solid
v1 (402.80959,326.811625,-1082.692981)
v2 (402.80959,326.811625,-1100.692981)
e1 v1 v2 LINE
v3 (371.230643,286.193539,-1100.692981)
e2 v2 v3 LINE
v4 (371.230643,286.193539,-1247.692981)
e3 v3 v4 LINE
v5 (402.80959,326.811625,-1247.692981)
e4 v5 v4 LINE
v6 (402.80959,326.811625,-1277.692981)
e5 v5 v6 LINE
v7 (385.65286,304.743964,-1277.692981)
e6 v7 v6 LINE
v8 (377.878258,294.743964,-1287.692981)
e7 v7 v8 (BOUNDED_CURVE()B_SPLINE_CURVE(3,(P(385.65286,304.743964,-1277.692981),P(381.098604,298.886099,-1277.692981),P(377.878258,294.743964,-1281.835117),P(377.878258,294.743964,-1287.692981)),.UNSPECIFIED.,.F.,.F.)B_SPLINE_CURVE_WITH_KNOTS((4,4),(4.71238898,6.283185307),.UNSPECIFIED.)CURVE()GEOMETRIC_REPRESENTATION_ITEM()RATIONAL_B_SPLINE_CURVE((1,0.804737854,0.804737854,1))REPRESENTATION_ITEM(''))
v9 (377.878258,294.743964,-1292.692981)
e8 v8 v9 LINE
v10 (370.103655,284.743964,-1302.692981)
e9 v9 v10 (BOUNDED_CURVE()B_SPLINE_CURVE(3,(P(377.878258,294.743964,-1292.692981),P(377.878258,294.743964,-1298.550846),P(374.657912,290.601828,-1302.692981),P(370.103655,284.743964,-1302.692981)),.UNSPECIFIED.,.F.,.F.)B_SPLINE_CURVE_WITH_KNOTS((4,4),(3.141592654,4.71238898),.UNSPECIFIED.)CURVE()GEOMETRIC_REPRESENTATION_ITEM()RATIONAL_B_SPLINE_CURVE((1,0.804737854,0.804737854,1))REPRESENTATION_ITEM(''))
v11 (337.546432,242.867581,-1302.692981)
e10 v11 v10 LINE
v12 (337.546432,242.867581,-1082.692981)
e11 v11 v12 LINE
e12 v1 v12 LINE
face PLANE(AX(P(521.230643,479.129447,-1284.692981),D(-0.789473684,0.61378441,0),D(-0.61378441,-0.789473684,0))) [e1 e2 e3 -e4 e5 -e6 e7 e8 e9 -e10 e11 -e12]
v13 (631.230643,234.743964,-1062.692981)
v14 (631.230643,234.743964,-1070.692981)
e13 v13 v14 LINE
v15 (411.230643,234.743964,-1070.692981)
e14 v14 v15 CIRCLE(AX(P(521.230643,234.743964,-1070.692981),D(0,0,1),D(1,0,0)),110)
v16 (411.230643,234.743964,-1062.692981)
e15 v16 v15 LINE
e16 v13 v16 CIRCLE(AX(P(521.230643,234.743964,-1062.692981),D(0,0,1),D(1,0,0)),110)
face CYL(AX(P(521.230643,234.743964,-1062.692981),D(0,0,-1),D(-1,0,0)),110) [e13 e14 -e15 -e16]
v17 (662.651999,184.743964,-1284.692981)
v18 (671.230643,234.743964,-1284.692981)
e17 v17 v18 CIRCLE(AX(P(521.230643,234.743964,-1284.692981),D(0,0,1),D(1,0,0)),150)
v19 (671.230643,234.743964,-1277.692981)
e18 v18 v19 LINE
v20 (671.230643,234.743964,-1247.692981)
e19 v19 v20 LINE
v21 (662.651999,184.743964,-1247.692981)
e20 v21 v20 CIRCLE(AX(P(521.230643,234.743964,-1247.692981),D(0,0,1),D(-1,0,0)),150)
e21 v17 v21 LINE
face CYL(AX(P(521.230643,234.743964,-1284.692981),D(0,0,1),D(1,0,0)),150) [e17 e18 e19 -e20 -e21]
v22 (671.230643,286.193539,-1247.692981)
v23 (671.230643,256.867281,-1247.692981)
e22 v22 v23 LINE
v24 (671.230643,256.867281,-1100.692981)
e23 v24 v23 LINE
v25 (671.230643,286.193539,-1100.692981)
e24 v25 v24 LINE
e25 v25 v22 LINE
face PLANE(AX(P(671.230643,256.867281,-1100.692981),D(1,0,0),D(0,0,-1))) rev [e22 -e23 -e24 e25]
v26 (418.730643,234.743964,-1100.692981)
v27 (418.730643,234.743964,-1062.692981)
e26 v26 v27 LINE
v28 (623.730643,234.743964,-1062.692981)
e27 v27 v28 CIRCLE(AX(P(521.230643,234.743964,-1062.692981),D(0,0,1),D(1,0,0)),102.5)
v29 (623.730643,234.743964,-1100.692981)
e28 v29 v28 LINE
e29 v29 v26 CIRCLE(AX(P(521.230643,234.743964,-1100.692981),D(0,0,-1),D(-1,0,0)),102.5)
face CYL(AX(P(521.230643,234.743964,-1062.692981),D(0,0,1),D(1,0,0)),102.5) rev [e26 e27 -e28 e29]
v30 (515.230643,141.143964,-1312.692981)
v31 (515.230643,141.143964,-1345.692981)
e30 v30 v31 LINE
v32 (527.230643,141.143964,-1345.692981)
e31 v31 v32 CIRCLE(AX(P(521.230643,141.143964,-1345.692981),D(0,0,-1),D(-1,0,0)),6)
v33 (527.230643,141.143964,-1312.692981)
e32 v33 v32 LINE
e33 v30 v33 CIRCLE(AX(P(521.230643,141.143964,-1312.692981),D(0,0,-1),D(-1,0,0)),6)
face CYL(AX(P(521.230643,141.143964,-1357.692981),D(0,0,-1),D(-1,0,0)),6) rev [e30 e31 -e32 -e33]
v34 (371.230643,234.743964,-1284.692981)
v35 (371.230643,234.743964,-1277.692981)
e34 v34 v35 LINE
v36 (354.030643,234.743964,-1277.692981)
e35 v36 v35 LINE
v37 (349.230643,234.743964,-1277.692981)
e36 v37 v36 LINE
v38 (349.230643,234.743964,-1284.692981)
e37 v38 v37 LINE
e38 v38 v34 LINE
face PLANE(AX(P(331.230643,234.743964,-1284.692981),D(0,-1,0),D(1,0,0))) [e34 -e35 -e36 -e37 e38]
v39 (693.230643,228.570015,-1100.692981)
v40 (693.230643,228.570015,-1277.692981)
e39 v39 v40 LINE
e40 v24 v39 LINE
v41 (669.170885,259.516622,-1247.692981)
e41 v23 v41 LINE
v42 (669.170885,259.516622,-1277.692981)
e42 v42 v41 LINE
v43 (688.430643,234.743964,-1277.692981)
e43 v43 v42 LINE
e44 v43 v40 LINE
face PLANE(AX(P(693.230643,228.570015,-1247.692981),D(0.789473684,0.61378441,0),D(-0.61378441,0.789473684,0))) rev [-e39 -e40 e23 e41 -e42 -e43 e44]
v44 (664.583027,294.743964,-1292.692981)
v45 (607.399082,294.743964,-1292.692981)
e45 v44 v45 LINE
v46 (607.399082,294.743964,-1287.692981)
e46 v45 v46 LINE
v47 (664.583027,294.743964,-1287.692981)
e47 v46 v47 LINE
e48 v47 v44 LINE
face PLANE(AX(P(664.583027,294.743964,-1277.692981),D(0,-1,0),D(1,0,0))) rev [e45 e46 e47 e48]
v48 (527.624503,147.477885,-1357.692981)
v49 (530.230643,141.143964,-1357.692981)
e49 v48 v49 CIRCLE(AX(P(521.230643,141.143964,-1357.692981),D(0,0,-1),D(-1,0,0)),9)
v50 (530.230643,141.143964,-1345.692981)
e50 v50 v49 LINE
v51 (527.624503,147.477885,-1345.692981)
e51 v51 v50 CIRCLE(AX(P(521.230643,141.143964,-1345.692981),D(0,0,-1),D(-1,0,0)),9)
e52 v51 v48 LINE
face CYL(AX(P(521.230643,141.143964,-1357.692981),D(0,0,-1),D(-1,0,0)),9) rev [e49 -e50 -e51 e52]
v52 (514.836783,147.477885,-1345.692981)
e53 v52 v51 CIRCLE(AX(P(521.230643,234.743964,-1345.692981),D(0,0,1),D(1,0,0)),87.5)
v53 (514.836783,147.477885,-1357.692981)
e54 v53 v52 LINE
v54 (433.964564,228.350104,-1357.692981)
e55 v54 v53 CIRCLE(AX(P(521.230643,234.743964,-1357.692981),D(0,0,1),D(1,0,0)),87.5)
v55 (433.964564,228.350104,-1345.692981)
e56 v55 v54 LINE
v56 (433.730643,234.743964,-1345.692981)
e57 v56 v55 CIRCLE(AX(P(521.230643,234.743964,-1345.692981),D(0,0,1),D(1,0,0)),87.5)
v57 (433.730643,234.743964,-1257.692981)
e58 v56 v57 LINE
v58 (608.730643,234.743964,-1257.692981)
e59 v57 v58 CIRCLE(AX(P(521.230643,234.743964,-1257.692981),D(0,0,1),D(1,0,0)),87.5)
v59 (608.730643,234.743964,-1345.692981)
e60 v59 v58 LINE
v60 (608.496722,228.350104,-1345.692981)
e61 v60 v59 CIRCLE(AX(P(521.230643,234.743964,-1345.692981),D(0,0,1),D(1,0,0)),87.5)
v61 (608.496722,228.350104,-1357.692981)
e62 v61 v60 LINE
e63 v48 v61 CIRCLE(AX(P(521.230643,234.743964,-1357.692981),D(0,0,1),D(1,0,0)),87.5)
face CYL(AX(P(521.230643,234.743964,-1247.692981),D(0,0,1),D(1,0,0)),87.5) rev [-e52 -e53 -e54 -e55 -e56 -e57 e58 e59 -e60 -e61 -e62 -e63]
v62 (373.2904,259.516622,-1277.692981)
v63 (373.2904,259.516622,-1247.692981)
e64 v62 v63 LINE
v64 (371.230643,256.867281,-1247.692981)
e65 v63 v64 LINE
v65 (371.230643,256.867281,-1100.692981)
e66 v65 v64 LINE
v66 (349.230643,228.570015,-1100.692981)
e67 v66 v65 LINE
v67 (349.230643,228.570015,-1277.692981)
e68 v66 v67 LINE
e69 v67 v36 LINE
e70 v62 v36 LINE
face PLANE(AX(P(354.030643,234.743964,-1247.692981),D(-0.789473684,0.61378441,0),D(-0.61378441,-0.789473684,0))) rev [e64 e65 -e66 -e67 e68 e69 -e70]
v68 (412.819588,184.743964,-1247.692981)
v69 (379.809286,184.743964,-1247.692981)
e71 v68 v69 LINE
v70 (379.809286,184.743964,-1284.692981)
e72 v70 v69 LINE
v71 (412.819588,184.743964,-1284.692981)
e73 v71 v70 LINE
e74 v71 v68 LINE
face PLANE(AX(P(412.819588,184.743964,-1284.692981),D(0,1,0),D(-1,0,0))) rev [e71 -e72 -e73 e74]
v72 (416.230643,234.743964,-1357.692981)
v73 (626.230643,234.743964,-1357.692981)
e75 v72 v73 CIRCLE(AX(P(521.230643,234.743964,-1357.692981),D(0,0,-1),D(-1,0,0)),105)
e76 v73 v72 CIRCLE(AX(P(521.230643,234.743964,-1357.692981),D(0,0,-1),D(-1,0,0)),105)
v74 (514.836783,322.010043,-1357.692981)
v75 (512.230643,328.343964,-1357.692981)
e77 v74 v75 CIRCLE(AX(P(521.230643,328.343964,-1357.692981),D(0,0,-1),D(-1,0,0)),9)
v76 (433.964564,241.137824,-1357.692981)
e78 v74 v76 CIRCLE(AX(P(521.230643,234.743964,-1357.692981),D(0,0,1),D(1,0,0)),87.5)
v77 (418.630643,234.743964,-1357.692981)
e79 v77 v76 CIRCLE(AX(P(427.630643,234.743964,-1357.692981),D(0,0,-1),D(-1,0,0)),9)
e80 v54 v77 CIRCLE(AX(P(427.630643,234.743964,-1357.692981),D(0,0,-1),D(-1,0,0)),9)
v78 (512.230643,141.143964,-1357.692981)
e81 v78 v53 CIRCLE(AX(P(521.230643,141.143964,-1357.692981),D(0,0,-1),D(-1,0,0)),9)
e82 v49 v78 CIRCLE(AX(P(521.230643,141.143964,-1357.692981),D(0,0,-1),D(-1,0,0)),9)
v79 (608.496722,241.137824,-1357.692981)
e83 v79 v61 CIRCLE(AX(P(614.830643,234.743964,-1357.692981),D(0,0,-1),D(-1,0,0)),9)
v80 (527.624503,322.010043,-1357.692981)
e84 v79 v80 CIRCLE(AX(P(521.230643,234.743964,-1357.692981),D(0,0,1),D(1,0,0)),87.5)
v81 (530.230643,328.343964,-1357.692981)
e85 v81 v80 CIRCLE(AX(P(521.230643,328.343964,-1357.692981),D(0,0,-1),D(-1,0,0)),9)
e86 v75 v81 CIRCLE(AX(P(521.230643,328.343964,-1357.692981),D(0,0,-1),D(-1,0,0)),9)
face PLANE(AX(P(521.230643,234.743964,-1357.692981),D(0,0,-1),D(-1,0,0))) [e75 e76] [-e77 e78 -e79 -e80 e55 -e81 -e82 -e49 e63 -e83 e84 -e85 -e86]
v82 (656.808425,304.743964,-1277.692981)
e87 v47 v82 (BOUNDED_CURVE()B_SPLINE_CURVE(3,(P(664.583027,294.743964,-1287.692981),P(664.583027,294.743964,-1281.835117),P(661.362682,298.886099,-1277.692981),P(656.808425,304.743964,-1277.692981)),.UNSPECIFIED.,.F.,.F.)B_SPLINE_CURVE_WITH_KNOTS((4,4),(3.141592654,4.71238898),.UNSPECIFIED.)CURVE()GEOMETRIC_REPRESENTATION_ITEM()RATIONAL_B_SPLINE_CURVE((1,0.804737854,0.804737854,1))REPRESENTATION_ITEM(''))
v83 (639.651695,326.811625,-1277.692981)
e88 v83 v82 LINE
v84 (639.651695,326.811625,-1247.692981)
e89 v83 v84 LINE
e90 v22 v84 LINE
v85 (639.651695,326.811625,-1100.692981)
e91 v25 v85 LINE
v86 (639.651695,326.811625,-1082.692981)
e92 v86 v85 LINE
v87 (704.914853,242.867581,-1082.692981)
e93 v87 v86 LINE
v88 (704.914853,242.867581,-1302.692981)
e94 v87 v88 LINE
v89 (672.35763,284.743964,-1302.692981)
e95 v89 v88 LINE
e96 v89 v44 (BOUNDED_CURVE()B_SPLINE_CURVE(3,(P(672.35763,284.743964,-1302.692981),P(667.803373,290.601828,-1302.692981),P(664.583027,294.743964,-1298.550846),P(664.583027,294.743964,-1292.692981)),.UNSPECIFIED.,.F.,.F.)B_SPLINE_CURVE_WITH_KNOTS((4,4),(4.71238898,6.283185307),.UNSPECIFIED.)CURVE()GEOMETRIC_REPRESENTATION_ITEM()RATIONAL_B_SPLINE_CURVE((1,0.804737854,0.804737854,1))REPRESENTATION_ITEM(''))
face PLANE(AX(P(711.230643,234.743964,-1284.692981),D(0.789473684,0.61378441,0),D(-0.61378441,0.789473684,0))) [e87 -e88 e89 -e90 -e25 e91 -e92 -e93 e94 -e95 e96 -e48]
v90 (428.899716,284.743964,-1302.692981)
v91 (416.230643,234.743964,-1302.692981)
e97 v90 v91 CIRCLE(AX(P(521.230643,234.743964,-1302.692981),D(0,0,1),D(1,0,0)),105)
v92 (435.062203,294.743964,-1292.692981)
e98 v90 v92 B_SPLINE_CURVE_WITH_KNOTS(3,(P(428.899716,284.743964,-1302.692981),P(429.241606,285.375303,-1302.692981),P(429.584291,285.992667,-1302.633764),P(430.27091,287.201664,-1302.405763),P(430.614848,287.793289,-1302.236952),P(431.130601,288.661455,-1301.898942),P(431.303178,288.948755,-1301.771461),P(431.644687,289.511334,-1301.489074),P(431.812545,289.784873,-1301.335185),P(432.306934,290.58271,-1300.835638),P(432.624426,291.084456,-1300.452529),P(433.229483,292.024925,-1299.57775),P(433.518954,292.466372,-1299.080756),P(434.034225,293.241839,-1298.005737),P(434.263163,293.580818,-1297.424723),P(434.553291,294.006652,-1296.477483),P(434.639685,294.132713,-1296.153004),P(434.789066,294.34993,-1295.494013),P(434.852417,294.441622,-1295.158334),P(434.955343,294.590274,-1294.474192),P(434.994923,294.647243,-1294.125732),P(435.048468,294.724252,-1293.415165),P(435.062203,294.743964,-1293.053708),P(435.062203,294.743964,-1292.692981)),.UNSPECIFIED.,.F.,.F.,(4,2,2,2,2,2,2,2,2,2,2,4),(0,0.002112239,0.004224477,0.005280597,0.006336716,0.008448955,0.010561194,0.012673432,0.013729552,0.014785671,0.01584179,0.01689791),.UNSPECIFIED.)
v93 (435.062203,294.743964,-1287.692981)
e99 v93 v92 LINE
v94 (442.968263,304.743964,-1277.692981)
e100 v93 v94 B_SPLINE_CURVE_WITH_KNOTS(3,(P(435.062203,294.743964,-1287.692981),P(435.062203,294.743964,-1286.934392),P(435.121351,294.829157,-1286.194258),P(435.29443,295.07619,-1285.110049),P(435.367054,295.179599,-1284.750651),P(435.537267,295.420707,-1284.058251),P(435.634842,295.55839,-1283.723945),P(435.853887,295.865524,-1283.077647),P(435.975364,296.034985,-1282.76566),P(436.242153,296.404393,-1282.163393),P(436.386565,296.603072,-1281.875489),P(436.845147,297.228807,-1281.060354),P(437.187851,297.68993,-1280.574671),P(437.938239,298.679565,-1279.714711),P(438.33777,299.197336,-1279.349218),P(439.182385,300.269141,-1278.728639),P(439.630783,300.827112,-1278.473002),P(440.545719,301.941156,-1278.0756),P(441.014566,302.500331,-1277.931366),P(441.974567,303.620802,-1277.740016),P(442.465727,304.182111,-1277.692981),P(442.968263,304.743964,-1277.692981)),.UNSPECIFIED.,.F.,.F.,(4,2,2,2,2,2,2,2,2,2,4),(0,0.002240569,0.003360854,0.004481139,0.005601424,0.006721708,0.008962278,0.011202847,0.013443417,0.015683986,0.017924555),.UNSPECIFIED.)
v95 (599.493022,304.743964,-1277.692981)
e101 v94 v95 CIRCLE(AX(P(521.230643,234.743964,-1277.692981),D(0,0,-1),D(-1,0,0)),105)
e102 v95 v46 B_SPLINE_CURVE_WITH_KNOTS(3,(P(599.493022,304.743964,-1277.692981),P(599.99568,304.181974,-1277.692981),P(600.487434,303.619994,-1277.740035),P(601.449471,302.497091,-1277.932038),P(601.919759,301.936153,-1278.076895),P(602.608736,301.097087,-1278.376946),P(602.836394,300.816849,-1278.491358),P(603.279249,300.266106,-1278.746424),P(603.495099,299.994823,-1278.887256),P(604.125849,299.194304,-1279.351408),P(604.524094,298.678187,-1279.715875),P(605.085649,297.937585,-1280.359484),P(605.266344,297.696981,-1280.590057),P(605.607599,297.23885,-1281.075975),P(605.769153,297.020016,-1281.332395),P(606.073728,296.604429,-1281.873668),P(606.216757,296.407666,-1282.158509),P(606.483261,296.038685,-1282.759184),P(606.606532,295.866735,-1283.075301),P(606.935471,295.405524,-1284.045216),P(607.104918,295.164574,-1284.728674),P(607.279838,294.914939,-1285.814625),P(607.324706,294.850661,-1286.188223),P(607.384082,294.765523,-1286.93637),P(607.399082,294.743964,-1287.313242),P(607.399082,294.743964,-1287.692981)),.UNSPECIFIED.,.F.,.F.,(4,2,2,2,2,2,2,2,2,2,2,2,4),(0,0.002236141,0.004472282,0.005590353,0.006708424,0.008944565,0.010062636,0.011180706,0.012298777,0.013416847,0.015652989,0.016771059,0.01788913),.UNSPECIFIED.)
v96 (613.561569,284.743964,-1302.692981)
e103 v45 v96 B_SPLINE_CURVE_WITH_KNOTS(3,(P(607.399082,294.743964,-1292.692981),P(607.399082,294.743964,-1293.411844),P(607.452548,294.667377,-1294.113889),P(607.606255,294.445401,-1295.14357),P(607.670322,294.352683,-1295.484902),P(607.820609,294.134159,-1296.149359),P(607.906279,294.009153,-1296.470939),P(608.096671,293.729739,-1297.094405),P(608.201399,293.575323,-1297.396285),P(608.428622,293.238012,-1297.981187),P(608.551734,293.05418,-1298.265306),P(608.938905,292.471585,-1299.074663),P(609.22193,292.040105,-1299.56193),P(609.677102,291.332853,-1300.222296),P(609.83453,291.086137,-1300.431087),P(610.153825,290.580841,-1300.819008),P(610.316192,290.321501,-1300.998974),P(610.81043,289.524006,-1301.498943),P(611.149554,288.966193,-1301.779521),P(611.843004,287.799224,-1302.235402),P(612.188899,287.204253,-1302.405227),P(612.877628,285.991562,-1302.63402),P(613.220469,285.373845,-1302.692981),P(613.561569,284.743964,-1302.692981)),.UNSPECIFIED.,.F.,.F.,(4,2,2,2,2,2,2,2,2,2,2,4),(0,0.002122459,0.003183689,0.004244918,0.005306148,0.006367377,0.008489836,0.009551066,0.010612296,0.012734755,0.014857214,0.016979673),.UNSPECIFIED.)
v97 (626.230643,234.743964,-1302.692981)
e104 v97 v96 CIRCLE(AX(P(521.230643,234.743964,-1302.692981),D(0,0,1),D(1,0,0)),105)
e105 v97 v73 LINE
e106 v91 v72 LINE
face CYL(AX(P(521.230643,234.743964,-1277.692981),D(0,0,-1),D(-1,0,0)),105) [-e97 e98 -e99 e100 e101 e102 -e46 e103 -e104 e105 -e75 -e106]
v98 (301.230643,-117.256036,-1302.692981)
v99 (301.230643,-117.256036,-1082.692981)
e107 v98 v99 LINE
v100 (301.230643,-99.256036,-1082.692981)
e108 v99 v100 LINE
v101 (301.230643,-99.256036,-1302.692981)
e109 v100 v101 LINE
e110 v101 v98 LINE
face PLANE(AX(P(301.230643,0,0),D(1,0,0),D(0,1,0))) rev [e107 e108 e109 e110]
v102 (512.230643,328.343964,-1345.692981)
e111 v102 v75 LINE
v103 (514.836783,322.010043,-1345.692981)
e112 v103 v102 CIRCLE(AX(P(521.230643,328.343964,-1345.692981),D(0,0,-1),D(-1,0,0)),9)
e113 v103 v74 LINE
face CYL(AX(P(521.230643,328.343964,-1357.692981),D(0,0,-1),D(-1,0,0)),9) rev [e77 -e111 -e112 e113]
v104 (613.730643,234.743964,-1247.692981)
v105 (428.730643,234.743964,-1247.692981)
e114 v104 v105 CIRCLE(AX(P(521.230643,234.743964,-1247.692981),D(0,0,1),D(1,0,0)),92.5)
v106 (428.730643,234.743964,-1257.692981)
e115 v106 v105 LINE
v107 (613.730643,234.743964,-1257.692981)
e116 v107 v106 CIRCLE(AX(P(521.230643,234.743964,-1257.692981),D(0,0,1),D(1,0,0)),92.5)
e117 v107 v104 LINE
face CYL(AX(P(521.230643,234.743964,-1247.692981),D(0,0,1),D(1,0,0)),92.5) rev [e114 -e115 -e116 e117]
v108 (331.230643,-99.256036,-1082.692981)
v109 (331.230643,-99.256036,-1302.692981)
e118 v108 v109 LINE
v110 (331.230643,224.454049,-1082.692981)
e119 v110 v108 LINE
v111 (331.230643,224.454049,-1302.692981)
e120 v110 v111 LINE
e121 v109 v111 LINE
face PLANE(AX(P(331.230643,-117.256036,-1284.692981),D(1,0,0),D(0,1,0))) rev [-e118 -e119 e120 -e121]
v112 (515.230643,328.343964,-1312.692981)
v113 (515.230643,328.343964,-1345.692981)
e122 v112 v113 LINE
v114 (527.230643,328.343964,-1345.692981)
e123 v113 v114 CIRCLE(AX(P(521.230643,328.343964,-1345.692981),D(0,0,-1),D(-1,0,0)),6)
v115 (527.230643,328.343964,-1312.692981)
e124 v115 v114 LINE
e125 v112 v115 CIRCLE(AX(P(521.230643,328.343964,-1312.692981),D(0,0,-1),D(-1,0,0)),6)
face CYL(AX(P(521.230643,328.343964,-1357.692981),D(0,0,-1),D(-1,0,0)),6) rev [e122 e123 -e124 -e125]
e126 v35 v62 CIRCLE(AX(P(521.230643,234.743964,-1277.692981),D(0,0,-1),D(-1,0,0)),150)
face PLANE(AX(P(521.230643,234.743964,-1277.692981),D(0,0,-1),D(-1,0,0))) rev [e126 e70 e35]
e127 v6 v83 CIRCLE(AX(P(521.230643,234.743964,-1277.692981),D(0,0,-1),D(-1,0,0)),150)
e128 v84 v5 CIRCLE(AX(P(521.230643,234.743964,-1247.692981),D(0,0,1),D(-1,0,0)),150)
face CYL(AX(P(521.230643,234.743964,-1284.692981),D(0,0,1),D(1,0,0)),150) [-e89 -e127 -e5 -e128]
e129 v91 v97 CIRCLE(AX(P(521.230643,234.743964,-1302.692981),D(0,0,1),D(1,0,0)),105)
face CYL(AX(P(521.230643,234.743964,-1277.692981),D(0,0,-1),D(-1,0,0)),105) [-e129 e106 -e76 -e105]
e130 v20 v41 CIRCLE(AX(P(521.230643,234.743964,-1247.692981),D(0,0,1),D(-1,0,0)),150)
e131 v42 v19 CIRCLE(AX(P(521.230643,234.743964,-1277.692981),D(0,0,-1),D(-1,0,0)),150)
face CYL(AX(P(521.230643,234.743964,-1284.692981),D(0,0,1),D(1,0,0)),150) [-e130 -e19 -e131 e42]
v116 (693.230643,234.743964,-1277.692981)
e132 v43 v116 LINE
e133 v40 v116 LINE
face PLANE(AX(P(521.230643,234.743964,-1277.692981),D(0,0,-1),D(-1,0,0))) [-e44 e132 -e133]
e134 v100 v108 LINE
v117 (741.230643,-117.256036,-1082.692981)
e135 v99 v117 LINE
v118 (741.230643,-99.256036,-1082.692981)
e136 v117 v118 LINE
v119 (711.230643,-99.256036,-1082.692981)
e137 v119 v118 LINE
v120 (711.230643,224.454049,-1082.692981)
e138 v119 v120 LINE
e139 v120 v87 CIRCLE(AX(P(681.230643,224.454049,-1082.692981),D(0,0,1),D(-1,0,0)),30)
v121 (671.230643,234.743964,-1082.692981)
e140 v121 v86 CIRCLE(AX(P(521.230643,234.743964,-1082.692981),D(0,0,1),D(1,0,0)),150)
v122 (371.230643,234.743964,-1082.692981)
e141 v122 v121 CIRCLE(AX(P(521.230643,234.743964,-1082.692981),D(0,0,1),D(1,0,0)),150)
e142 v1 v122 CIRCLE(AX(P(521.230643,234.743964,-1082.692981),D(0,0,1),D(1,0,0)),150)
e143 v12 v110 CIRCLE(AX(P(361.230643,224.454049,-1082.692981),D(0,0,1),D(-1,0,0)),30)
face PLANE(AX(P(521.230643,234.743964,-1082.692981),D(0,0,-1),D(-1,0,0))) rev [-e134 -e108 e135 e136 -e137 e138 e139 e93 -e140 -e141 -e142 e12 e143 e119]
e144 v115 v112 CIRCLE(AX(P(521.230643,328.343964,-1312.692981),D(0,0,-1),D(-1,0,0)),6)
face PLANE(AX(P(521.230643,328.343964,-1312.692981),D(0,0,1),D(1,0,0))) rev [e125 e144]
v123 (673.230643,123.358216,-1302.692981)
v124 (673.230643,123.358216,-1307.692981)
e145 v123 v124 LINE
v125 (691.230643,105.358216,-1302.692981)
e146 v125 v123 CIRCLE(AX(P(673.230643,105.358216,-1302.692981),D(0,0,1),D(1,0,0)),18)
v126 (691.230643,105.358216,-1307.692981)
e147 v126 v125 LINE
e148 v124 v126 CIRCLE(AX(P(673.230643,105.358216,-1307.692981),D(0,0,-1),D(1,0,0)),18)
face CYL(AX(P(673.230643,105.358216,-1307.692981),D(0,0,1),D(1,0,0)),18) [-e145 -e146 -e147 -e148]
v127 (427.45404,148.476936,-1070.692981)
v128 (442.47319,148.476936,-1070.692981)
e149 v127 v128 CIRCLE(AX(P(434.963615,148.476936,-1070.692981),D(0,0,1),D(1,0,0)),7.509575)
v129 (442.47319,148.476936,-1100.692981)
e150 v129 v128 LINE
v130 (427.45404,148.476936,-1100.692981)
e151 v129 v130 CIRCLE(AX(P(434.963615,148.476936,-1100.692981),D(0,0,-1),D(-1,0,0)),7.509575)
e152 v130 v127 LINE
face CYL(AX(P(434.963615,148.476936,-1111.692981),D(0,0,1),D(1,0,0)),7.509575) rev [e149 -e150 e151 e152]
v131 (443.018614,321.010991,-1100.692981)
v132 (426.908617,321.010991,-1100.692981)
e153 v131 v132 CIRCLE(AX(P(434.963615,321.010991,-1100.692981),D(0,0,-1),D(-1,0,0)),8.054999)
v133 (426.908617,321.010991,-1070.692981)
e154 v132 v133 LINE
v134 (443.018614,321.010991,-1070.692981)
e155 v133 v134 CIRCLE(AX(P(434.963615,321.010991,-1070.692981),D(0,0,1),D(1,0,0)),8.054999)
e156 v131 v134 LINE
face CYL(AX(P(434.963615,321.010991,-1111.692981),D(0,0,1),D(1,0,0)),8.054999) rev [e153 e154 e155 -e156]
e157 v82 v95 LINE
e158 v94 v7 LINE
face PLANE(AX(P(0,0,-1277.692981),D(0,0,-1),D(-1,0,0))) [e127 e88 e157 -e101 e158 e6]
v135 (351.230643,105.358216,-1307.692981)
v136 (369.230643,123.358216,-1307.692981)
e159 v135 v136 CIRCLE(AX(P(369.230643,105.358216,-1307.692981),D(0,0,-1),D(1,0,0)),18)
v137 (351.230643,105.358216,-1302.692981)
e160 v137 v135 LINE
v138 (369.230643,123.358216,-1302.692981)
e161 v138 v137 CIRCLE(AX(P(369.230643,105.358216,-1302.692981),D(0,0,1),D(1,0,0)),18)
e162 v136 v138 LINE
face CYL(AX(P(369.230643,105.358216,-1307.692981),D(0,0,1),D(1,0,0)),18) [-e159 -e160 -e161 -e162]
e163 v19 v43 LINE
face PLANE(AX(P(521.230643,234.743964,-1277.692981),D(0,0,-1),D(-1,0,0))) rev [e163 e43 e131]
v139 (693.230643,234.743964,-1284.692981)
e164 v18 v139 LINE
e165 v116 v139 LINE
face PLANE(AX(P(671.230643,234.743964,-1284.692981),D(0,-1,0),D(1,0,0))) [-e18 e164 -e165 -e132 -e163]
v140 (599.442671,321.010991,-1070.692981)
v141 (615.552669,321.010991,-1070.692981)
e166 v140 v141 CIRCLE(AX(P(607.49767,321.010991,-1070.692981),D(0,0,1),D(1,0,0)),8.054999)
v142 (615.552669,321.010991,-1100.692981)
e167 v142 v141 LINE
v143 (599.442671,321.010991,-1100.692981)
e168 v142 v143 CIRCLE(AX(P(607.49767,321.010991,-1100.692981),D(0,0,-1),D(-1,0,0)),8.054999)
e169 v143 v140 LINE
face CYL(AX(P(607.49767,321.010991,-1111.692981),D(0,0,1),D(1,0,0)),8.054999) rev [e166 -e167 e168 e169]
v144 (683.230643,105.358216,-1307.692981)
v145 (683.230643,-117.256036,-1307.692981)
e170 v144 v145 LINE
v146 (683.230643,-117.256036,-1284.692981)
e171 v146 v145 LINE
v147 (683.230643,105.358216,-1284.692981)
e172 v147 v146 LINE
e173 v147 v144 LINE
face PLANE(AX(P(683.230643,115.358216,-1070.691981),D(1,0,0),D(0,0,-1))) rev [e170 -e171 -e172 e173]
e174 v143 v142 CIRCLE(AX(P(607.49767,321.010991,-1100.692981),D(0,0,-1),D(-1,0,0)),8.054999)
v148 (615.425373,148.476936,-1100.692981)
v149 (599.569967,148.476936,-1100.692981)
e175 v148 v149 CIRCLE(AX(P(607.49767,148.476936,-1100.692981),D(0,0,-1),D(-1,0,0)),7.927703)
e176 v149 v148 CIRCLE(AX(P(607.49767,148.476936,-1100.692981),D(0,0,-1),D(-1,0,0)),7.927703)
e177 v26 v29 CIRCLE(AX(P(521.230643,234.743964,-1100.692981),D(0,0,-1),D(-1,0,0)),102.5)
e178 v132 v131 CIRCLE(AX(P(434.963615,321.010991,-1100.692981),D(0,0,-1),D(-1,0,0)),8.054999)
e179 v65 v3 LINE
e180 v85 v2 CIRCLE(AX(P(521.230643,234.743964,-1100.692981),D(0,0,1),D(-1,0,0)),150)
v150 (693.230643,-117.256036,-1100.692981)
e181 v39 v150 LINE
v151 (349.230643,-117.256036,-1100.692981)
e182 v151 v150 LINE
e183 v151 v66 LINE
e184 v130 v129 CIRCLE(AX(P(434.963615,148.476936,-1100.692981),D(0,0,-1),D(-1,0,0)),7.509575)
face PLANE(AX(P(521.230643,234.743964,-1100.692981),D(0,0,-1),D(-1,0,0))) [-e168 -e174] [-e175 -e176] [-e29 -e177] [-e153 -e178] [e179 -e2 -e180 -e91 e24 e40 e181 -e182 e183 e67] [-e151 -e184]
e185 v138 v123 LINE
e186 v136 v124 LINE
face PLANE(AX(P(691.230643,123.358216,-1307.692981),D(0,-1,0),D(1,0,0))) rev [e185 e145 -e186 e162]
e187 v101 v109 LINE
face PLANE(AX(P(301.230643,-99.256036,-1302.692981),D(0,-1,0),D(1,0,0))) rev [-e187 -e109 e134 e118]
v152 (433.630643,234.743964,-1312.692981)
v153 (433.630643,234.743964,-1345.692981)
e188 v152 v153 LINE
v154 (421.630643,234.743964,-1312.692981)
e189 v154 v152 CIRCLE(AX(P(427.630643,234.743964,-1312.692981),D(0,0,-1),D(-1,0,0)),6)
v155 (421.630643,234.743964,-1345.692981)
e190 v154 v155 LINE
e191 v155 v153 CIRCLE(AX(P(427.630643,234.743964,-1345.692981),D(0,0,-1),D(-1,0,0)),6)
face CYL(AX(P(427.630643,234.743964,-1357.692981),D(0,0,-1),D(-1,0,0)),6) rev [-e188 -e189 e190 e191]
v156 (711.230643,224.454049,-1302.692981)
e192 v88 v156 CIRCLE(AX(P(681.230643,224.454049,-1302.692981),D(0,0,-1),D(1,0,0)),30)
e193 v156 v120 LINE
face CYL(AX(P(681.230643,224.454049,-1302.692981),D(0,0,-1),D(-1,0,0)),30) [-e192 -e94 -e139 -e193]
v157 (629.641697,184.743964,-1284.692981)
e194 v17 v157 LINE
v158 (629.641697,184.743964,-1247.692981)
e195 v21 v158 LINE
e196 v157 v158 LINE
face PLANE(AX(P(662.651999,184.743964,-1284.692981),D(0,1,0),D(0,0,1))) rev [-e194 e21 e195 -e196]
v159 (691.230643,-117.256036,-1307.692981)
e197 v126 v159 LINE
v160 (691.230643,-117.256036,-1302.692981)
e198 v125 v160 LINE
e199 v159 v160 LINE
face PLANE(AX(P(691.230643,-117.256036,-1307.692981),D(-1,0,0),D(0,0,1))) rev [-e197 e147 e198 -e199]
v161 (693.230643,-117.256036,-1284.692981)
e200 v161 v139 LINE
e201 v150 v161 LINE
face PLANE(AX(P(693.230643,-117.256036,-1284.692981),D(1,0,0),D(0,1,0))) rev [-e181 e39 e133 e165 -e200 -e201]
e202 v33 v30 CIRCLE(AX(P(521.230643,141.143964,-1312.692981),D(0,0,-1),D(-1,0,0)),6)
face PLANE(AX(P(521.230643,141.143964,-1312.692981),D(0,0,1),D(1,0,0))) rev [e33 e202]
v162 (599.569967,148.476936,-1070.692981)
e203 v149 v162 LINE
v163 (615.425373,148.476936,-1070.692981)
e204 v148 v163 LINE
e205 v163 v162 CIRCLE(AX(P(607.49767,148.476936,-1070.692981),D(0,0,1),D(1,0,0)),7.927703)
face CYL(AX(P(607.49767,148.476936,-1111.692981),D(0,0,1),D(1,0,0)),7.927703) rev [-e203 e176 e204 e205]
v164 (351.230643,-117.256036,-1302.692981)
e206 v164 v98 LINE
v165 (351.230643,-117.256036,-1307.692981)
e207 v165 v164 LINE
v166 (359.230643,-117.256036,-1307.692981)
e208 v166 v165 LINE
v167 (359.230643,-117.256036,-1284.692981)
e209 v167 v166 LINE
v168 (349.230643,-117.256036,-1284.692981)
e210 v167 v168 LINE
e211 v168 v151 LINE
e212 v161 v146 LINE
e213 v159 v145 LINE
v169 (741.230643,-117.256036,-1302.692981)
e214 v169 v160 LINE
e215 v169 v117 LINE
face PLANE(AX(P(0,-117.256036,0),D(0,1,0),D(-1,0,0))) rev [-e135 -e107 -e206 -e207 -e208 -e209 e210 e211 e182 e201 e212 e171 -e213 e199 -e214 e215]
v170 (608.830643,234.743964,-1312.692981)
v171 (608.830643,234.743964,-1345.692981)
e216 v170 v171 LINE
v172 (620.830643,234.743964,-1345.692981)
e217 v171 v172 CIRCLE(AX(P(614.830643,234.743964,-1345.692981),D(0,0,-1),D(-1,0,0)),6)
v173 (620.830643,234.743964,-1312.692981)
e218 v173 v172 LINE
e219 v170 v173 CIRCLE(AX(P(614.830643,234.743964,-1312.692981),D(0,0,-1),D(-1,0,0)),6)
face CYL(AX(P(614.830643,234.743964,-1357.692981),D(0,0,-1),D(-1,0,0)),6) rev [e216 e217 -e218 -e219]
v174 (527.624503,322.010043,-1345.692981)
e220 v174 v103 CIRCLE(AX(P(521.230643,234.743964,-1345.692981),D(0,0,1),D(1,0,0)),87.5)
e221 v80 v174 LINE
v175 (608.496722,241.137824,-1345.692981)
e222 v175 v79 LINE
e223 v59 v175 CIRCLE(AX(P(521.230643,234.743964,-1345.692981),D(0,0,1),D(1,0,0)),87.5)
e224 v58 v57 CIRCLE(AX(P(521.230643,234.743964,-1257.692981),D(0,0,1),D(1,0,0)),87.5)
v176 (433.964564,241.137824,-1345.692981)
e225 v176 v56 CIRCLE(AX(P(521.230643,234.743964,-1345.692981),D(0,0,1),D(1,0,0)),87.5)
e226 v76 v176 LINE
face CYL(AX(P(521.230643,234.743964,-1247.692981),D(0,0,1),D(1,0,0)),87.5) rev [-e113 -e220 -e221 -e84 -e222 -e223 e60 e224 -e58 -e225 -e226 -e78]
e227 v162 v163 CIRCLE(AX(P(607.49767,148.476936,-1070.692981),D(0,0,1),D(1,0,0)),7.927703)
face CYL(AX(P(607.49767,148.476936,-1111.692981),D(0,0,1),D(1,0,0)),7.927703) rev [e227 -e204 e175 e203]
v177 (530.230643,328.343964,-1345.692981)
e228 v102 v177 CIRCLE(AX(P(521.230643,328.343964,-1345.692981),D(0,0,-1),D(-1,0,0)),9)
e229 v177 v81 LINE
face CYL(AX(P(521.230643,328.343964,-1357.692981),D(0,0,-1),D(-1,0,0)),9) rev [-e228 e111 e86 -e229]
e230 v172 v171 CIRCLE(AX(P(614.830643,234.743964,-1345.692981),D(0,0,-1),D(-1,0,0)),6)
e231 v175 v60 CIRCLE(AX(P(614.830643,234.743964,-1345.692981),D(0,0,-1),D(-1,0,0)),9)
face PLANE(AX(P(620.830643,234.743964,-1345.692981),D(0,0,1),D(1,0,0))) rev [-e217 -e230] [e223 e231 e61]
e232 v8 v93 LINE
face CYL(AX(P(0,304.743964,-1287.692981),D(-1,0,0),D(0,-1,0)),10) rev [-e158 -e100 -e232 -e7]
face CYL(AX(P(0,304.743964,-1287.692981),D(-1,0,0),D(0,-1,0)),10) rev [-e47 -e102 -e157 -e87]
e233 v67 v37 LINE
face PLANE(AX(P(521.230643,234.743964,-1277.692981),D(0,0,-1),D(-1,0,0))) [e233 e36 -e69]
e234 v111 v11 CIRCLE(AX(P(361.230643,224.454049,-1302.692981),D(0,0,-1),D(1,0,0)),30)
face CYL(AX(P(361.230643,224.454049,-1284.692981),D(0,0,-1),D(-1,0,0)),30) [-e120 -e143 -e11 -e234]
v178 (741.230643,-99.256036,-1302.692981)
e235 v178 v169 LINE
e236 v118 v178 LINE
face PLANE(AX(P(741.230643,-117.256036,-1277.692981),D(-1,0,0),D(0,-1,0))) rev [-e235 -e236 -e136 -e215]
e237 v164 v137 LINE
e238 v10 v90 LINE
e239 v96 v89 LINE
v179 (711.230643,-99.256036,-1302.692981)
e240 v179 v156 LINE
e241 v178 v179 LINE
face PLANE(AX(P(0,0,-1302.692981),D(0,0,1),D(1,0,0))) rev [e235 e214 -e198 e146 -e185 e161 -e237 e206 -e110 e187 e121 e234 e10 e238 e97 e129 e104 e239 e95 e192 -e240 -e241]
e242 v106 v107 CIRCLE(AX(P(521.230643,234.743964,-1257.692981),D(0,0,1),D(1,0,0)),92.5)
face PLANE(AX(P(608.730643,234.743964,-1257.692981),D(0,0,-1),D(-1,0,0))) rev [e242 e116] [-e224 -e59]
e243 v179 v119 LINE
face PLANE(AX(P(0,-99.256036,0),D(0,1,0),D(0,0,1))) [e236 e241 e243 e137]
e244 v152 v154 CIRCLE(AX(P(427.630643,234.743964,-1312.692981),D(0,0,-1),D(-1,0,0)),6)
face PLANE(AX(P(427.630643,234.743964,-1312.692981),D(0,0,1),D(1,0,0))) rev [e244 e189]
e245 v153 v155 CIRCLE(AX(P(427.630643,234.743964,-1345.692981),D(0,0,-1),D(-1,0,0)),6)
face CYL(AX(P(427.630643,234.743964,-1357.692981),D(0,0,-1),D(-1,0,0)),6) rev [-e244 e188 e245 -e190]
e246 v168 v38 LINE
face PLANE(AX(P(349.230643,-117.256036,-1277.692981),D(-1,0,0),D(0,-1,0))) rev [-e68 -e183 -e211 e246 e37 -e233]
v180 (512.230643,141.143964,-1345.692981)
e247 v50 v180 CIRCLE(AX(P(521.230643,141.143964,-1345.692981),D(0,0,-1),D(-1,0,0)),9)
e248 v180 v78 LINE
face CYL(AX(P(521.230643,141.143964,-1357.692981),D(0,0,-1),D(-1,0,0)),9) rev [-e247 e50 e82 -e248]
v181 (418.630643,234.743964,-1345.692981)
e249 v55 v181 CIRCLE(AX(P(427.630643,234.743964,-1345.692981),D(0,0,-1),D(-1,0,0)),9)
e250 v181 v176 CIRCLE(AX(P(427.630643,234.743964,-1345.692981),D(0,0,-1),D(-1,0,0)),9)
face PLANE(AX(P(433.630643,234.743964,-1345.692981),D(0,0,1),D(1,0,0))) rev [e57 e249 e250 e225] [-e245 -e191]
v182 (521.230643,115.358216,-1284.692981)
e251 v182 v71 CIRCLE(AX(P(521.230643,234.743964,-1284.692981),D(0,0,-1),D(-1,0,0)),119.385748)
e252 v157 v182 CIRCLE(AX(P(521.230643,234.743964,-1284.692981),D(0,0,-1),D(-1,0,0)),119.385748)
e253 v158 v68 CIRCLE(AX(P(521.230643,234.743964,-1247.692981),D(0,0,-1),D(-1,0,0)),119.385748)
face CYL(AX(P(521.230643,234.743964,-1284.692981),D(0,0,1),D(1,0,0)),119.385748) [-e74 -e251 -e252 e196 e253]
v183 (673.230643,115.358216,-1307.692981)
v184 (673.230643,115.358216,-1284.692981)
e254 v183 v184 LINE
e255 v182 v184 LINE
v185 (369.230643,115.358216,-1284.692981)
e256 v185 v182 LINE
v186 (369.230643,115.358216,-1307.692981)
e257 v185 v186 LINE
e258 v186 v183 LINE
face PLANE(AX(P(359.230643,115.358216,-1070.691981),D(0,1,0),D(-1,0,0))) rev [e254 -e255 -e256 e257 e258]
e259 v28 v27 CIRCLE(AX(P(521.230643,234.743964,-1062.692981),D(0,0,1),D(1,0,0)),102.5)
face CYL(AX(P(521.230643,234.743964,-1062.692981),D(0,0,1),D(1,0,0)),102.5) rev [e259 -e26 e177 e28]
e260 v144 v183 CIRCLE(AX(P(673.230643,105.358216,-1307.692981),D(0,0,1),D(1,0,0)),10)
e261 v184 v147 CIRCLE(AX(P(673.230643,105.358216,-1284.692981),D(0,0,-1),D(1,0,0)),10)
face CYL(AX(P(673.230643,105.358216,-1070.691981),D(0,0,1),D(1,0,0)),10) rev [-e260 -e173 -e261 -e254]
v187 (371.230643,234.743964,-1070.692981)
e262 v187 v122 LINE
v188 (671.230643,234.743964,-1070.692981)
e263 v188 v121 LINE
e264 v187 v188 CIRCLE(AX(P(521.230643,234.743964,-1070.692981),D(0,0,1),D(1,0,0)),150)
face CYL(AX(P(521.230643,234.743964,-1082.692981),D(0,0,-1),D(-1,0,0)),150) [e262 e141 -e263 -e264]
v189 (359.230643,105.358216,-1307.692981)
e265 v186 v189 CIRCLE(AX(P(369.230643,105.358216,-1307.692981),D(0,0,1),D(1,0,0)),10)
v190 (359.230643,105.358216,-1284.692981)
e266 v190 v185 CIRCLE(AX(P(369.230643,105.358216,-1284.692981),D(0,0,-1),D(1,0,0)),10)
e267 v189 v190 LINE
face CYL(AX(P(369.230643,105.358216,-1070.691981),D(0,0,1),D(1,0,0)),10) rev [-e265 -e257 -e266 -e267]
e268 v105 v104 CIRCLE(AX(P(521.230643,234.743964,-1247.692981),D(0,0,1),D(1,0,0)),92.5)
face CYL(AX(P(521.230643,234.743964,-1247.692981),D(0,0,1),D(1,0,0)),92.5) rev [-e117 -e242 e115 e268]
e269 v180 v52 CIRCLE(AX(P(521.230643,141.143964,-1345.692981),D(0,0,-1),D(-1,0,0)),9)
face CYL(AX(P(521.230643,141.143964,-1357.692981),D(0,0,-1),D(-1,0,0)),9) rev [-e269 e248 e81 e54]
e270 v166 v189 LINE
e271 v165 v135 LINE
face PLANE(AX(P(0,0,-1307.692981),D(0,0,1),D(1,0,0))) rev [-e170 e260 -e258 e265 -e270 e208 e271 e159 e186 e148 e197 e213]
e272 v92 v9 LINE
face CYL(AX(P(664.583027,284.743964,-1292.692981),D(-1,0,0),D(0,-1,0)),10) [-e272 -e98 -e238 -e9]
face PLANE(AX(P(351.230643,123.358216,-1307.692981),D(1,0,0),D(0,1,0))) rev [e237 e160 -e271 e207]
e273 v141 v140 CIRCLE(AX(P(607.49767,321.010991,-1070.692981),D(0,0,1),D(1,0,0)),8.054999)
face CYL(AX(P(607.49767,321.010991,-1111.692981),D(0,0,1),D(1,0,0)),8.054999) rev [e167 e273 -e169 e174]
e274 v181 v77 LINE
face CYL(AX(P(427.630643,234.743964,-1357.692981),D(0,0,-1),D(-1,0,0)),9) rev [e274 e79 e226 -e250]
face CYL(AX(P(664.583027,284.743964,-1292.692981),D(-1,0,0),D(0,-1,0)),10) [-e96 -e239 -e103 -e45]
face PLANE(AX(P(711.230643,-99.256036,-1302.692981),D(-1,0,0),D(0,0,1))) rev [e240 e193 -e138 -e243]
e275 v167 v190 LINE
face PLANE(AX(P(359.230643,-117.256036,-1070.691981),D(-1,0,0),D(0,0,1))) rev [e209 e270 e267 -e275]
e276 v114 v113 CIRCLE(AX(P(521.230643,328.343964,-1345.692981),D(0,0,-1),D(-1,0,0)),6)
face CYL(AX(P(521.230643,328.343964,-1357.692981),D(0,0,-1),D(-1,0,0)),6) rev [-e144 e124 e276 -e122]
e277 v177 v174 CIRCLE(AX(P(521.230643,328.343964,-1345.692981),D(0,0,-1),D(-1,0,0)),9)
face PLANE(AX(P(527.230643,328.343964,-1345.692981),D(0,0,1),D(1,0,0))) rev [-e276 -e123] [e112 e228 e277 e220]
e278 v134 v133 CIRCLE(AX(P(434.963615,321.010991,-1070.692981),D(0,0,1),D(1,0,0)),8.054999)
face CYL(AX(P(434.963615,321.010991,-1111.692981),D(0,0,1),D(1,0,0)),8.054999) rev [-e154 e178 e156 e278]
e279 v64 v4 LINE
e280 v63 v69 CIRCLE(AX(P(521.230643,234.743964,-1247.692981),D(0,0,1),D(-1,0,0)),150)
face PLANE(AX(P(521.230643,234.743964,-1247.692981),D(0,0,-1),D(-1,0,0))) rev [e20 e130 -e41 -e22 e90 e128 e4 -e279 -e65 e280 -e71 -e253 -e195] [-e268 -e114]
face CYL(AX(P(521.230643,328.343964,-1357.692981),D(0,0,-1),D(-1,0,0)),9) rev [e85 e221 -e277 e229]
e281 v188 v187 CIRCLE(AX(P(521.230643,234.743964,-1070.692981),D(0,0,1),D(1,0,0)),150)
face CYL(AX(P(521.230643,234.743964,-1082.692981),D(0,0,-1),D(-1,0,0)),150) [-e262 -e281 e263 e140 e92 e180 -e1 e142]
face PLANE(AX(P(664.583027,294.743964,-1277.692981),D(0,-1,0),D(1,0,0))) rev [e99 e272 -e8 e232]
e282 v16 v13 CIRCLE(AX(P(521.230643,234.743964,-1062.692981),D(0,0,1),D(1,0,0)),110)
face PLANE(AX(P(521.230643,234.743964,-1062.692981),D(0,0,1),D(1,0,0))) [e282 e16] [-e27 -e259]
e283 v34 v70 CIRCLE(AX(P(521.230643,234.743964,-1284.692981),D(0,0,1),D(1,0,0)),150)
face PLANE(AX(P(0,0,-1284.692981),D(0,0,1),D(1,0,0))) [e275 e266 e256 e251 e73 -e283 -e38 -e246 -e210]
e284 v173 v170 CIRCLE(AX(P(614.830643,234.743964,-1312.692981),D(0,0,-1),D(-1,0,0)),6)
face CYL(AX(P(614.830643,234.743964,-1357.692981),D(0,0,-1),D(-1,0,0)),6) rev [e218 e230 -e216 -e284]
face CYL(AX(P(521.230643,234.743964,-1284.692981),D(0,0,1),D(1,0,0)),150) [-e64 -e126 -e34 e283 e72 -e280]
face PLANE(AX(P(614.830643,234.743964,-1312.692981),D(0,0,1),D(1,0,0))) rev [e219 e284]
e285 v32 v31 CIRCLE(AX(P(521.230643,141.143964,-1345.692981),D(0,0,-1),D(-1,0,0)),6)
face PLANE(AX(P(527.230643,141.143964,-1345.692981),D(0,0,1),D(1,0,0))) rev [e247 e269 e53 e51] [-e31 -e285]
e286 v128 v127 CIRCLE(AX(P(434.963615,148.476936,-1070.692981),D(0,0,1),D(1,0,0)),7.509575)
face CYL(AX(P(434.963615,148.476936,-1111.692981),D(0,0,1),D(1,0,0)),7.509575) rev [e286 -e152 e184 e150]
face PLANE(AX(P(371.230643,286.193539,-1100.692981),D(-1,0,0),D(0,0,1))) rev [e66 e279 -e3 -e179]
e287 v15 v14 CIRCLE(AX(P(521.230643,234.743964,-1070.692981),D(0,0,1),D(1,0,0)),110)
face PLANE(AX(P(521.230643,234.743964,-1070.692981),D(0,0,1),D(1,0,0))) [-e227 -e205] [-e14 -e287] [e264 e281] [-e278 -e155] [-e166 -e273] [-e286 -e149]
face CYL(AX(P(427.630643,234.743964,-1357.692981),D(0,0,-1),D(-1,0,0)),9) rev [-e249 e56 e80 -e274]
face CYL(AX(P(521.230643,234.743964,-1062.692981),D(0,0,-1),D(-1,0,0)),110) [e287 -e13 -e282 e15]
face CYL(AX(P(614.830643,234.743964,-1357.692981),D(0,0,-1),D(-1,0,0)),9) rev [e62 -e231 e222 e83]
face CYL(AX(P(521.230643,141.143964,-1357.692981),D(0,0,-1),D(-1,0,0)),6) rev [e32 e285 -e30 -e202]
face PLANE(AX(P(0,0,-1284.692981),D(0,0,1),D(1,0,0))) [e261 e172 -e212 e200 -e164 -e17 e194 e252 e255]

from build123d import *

# Parameters (mm, degrees)
BOSS_EXTRUDE1_DEPTH               = 7
SKETCH2_W                         = 48
SKETCH2_H                         = 7
BOSS_EXTRUDE2_DEPTH               = 352
SKETCH3_W                         = 18
SKETCH3_H                         = 7
BOSS_EXTRUDE3_DEPTH               = 352
BOSS_EXTRUDE4_DEPTH               = 18
BOSS_EXTRUDE5_START               = 30
BOSS_EXTRUDE5_DEPTH               = 30
BOSS_EXTRUDE6_DEPTH               = 147
BOSS_EXTRUDE7_DEPTH               = 147
BOSS_EXTRUDE8_START               = 18
BOSS_EXTRUDE8_DEPTH               = 18
SKETCH9_W                         = 30
SKETCH9_H                         = 220
CUT_EXTRUDE1_DEPTH                = 334
CUT_EXTRUDE2_DEPTH                = 30
CUT_EXTRUDE3_DEPTH                = 30
SKETCH12_W                        = 220
SKETCH12_H                        = 18
BOSS_EXTRUDE9_DEPTH               = 30
BOSS_EXTRUDE10_START              = 12
SKETCH13_R                        = 150
BOSS_EXTRUDE10_DEPTH              = 12
CUT_EXTRUDE4_DEPTH                = 37
SKETCH15_W                        = 340
SKETCH15_H                        = 240.614252285
BOSS_EXTRUDE11_DEPTH              = 5
CUT_EXTRUDE5_REACH                = 915.869
SKETCH16_W                        = 324
SKETCH16_H                        = 232.614252285
CUT_EXTRUDE6_DEPTH                = 25
SKETCH18_R                        = 110
BOSS_EXTRUDE12_DEPTH              = 8
SKETCH19_W                        = 105
SKETCH19_H                        = 80
HOLE1_D                           = 205
HOLE1_DEPTH                       = 38
M10_COUNTERBORE_HOLE1_D           = 12
M10_COUNTERBORE_HOLE1_DEPTH       = 45
M10_COUNTERBORE_HOLE1_CBORE_D     = 18
M10_COUNTERBORE_HOLE1_CBORE_DEPTH = 12
HOLE2_D                           = 175
HOLE2_CBORE_D                     = 185
HOLE2_CBORE_DEPTH                 = 10
FILLET1_R                         = 10
FILLET2_R                         = 18
FILLET3_R                         = 30
FILLET4_R                         = 150
SKETCH26_R                        = 8.054998693
SKETCH26_R_2                      = 7.927703382
SKETCH26_R_3                      = 7.509574851
CUT_EXTRUDE8_DEPTH                = 41


with BuildPart() as part:
    # Sketch1 → Boss-Extrude1 (new body)
    with BuildSketch(Plane.XY.offset(-1277.692981355)):
        with BuildLine():
            Line((671.230642584, 234.743963655), (711.230642584, 234.743963655))
            Line((711.230642584, 234.743963655), (521.230642584, 479.129447483))
            Line((521.230642584, 479.129447483), (331.230642584, 234.743963655))
            Line((331.230642584, 234.743963655), (371.230642584, 234.743963655))
            ThreePointArc((371.230642584, 234.743963655), (521.230642584, 84.743963655), (671.230642584, 234.743963655))
        make_face()
    extrude(amount=-BOSS_EXTRUDE1_DEPTH)

    # Sketch2 → Boss-Extrude2 (add)
    with BuildSketch(Plane.XZ.offset(-234.743963655)):
        with Locations((717.230642584, -1281.192981355)):
            Rectangle(SKETCH2_W, SKETCH2_H)
    extrude(amount=BOSS_EXTRUDE2_DEPTH)

    # Sketch3 → Boss-Extrude3 (add)
    with BuildSketch(Plane.XZ.offset(-234.743963654)):
        with Locations((340.230642584, -1281.192981355)):
            Rectangle(SKETCH3_W, SKETCH3_H)
    extrude(amount=BOSS_EXTRUDE3_DEPTH)

    # Sketch4 → Boss-Extrude4 (add)
    with BuildSketch(Plane(origin=(0, 0, -1284.692981355), x_dir=(-1, 0, 0), z_dir=(0, 0, -1))):
        Polygon((-331.230642584, -117.256036345), (-741.230642584, -117.256036345), (-741.230642584, 234.743963655), (-711.230642584, 234.743963655), (-521.230642584, 479.129447483), (-331.230642584, 234.743963655), align=None)
    extrude(amount=BOSS_EXTRUDE4_DEPTH)

    # Sketch5 → Boss-Extrude5 (add)
    with BuildSketch(Plane.XY.offset(-1277.692981355).offset(BOSS_EXTRUDE5_START)):
        with BuildLine():
            Line((371.230642584, 234.743963655), (354.030642584, 234.743963655))
            Line((354.030642584, 234.743963655), (349.230642584, 228.570014589))
            Line((349.230642584, 228.570014589), (349.230642584, -117.256036345))
            Line((349.230642584, -117.256036345), (331.230642584, -117.256036345))
            Line((331.230642584, -117.256036345), (331.230642584, 234.743963655))
            Line((331.230642584, 234.743963655), (521.230642584, 479.129447483))
            Line((521.230642584, 479.129447483), (711.230642584, 234.743963655))
            Line((711.230642584, 234.743963655), (741.230642584, 234.743963655))
            Line((741.230642584, 234.743963655), (741.230642584, -117.256036345))
            Line((741.230642584, -117.256036345), (693.230642584, -117.256036345))
            Line((693.230642584, -117.256036345), (693.230642584, 228.570014589))
            Line((693.230642584, 228.570014589), (688.430642584, 234.743963655))
            Line((688.430642584, 234.743963655), (671.230642584, 234.743963655))
            ThreePointArc((671.230642584, 234.743963655), (521.230642584, 84.743963655), (371.230642584, 234.743963655))
        make_face()
    extrude(amount=-BOSS_EXTRUDE5_DEPTH)

    # Sketch6 → Boss-Extrude6 (add)
    with BuildSketch(Plane.XY.offset(-1247.692981355)):
        Polygon((371.230642584, 256.867281138), (349.230642584, 228.570014589), (349.230642584, -117.256036345), (331.230642584, -117.256036345), (331.230642584, 234.743963655), (371.230642584, 286.193539197), align=None)
    extrude(amount=BOSS_EXTRUDE6_DEPTH)

    # Sketch7 → Boss-Extrude7 (add)
    with BuildSketch(Plane.XY.offset(-1247.692981355)):
        Polygon((741.230642584, -117.256036345), (693.230642584, -117.256036345), (693.230642584, 228.570014589), (671.230642584, 256.867281138), (671.230642584, 286.193539197), (711.230642584, 234.743963655), (741.230642584, 234.743963655), align=None)
    extrude(amount=BOSS_EXTRUDE7_DEPTH)

    # Sketch8 → Boss-Extrude8 (add)
    with BuildSketch(Plane.XY.offset(-1100.692981355).offset(BOSS_EXTRUDE8_START)):
        with BuildLine():
            Line((331.230642584, -117.256036345), (331.230642584, 234.743963654))
            Line((331.230642584, 234.743963654), (402.809589953, 326.811625152))
            ThreePointArc((402.809589953, 326.811625152), (521.230642584, 384.743963654), (639.651695216, 326.811625152))
            Line((639.651695216, 326.811625152), (711.230642584, 234.743963654))
            Line((711.230642584, 234.743963654), (741.230642584, 234.743963654))
            Line((741.230642584, 234.743963654), (741.230642584, -117.256036345))
            Line((741.230642584, -117.256036345), (331.230642584, -117.256036345))
        make_face()
    extrude(amount=-BOSS_EXTRUDE8_DEPTH)

    # Sketch9 → Cut-Extrude1 (cut)
    with BuildSketch(Plane(origin=(0, 234.743963655, 0), x_dir=(-1, 0, 0), z_dir=(0, 1, 0))):
        with Locations((-726.230642584, -1192.692981355)):
            Rectangle(SKETCH9_W, SKETCH9_H)
    extrude(amount=-CUT_EXTRUDE1_DEPTH, mode=Mode.SUBTRACT)

    # Sketch10 → Cut-Extrude2 (cut)
    with BuildSketch(Plane.XY.offset(-1247.692981355)):
        with BuildLine():
            Line((671.230642584, 234.743963655), (688.430642584, 234.743963655))
            Line((688.430642584, 234.743963655), (669.170885211, 259.516622202))
            ThreePointArc((669.170885211, 259.516622202), (670.714816319, 247.173034536), (671.230642584, 234.743963655))
        make_face()
    extrude(amount=-CUT_EXTRUDE2_DEPTH, mode=Mode.SUBTRACT)

    # Sketch11 → Cut-Extrude3 (cut)
    with BuildSketch(Plane.XY.offset(-1247.692981355)):
        with BuildLine():
            Line((373.290399958, 259.516622202), (354.030642584, 234.743963655))
            Line((354.030642584, 234.743963655), (371.230642584, 234.743963655))
            ThreePointArc((371.230642584, 234.743963655), (371.74646885, 247.173034536), (373.290399958, 259.516622202))
        make_face()
    extrude(amount=-CUT_EXTRUDE3_DEPTH, mode=Mode.SUBTRACT)

    # Sketch12 → Boss-Extrude9 (add)
    with BuildSketch(Plane.ZY.offset(-331.230642584)):
        with Locations((-1192.692981355, -108.256036346)):
            Rectangle(SKETCH12_W, SKETCH12_H)
    extrude(amount=BOSS_EXTRUDE9_DEPTH)

    # Sketch13 → Boss-Extrude10 (add)
    with BuildSketch(Plane.XY.offset(-1082.692981355).offset(BOSS_EXTRUDE10_START)):
        with Locations(Location((521.230642584, 234.743963655, 0), (0, 0, 142.136353638))):
            Circle(SKETCH13_R)
    extrude(amount=-BOSS_EXTRUDE10_DEPTH)

    # Sketch14 → Cut-Extrude4 (cut)
    with BuildSketch(Plane.XY.offset(-1247.692981355)):
        with BuildLine():
            Line((412.819587994, 184.743963655), (379.809286347, 184.743963655))
            ThreePointArc((379.809286347, 184.743963655), (521.230642584, 84.743963655), (662.651998822, 184.743963655))
            Line((662.651998822, 184.743963655), (629.641697174, 184.743963655))
            ThreePointArc((629.641697174, 184.743963655), (521.230642584, 115.35821594), (412.819587994, 184.743963655))
        make_face()
    extrude(amount=-CUT_EXTRUDE4_DEPTH, mode=Mode.SUBTRACT)

    # Sketch15 → Boss-Extrude11 (add)
    with BuildSketch(Plane(origin=(0, 0, -1302.692981355), x_dir=(-1, 0, 0), z_dir=(0, 0, -1))):
        with Locations((-521.230642584, 3.051089797)):
            Rectangle(SKETCH15_W, SKETCH15_H)
    extrude(amount=BOSS_EXTRUDE11_DEPTH)

    # Sketch16 → Cut-Extrude5 (cut, up to next)
    with BuildSketch(Plane(origin=(0, 0, -1307.692981355), x_dir=(-1, 0, 0), z_dir=(0, 0, -1)), mode=Mode.PRIVATE) as cut_extrude5_sk1:
        with Locations((-521.230642584, -0.948910203)):
            Rectangle(SKETCH16_W, SKETCH16_H)
    cut_extrude5_tool1 = extrude(cut_extrude5_sk1.sketch, amount=-CUT_EXTRUDE5_REACH, mode=Mode.PRIVATE) & part.part
    add(cut_extrude5_tool1.solids().sort_by_distance((521.230643, -0.94891, -1307.692981))[0], mode=Mode.SUBTRACT)

    # Sketch17 → Cut-Extrude6 (cut)
    with BuildSketch(Plane(origin=(0, 0, -1302.692981355), x_dir=(-1, 0, 0), z_dir=(0, 0, -1))):
        Polygon((-521.230642584, 479.129447483), (-664.583027426, 294.743963655), (-377.878257743, 294.743963655), align=None)
    extrude(amount=-CUT_EXTRUDE6_DEPTH, mode=Mode.SUBTRACT)

    # Sketch18 → Boss-Extrude12 (add)
    with BuildSketch(Plane.XY.offset(-1070.692981355)):
        with Locations((521.230642584, 234.743963655)):
            Circle(SKETCH18_R)
    extrude(amount=BOSS_EXTRUDE12_DEPTH)

    # Sketch19 → Revolve1 (revolve)
    with BuildSketch(Plane(origin=(280.2795082, 402.520798349, 0), x_dir=(-0.8206518066482866, 0.5714285714285761, 0), z_dir=(0.5714285714285761, 0.8206518066482866, 0)), mode=Mode.PRIVATE) as revolve1_sk:
        with Locations((-241.109460715, -1317.692981355)):
            Rectangle(SKETCH19_W, SKETCH19_H)
    revolve(revolve1_sk.sketch.rotate(Axis((521.230642584, 234.743963655, -1277.692981355), (0, 0, -1)), 325.150095421), axis=Axis((521.230642584, 234.743963655, -1277.692981355), (0, 0, -1)))

    # Hole1
    with Locations(Plane.XY.offset(-1062.692981355)):
        with Locations((521.230642584, 234.743963655)):
            Hole(HOLE1_D / 2, depth=HOLE1_DEPTH)

    # M10 counterbore hole1
    with Locations(Plane(origin=(0, 0, -1357.692981355), x_dir=(-1, 0, 0), z_dir=(0, 0, -1))):
        with Locations((-614.830642584, 234.743963655), (-521.230642584, 141.143963655), (-427.630642584, 234.743963655), (-521.230642584, 328.343963655)):
            CounterBoreHole(M10_COUNTERBORE_HOLE1_D / 2, M10_COUNTERBORE_HOLE1_CBORE_D / 2, M10_COUNTERBORE_HOLE1_CBORE_DEPTH, depth=M10_COUNTERBORE_HOLE1_DEPTH)

    # Hole2 (through all)
    with Locations(Plane.XY.offset(-1247.692981355)):
        with Locations((521.230642584, 234.743963655)):
            CounterBoreHole(HOLE2_D / 2, HOLE2_CBORE_D / 2, HOLE2_CBORE_DEPTH)

    # Fillet1
    fillet1_edges = [part.edges().sort_by_distance(p)[0] for p in [
        (683.230642584, 115.35821594, -1296.192981355),
        (359.230642584, 115.35821594, -1296.192981355),
        (635.991054854, 294.743963655, -1277.692981355),
        (635.991054854, 294.743963655, -1302.692981355),
        (406.470230315, 294.743963655, -1277.692981355),
        (406.470230315, 294.743963655, -1302.692981355),
    ]]
    fillet(fillet1_edges, radius=FILLET1_R)

    # Fillet2
    fillet2_edges = [part.edges().sort_by_distance(p)[0] for p in [
        (351.230642584, 123.35821594, -1305.192981355),
        (691.230642584, 123.35821594, -1305.192981355),
    ]]
    fillet(fillet2_edges, radius=FILLET2_R)

    # Fillet3
    fillet3_edges = [part.edges().sort_by_distance(p)[0] for p in [
        (331.230642584, 234.743963654, -1192.692981355),
        (711.230642584, 234.743963654, -1192.692981355),
    ]]
    fillet(fillet3_edges, radius=FILLET3_R)

    # Fillet4
    fillet4_edges = [part.edges().sort_by_distance(p)[0] for p in [
        (521.230642584, 479.129447483, -1262.692981355),
    ]]
    fillet(fillet4_edges, radius=FILLET4_R)

    # Sketch26 → Cut-Extrude8 (cut)
    with BuildSketch(Plane.XY.offset(-1070.692981355)):
        with Locations((434.96361528, 321.010990959)):
            Circle(SKETCH26_R)
        with Locations((607.497669889, 321.010990959)):
            Circle(SKETCH26_R)
        with Locations((607.497669889, 148.47693635)):
            Circle(SKETCH26_R_2)
        with Locations((434.96361528, 148.47693635)):
            Circle(SKETCH26_R_3)
    extrude(amount=-CUT_EXTRUDE8_DEPTH, mode=Mode.SUBTRACT)


solid = part.part
